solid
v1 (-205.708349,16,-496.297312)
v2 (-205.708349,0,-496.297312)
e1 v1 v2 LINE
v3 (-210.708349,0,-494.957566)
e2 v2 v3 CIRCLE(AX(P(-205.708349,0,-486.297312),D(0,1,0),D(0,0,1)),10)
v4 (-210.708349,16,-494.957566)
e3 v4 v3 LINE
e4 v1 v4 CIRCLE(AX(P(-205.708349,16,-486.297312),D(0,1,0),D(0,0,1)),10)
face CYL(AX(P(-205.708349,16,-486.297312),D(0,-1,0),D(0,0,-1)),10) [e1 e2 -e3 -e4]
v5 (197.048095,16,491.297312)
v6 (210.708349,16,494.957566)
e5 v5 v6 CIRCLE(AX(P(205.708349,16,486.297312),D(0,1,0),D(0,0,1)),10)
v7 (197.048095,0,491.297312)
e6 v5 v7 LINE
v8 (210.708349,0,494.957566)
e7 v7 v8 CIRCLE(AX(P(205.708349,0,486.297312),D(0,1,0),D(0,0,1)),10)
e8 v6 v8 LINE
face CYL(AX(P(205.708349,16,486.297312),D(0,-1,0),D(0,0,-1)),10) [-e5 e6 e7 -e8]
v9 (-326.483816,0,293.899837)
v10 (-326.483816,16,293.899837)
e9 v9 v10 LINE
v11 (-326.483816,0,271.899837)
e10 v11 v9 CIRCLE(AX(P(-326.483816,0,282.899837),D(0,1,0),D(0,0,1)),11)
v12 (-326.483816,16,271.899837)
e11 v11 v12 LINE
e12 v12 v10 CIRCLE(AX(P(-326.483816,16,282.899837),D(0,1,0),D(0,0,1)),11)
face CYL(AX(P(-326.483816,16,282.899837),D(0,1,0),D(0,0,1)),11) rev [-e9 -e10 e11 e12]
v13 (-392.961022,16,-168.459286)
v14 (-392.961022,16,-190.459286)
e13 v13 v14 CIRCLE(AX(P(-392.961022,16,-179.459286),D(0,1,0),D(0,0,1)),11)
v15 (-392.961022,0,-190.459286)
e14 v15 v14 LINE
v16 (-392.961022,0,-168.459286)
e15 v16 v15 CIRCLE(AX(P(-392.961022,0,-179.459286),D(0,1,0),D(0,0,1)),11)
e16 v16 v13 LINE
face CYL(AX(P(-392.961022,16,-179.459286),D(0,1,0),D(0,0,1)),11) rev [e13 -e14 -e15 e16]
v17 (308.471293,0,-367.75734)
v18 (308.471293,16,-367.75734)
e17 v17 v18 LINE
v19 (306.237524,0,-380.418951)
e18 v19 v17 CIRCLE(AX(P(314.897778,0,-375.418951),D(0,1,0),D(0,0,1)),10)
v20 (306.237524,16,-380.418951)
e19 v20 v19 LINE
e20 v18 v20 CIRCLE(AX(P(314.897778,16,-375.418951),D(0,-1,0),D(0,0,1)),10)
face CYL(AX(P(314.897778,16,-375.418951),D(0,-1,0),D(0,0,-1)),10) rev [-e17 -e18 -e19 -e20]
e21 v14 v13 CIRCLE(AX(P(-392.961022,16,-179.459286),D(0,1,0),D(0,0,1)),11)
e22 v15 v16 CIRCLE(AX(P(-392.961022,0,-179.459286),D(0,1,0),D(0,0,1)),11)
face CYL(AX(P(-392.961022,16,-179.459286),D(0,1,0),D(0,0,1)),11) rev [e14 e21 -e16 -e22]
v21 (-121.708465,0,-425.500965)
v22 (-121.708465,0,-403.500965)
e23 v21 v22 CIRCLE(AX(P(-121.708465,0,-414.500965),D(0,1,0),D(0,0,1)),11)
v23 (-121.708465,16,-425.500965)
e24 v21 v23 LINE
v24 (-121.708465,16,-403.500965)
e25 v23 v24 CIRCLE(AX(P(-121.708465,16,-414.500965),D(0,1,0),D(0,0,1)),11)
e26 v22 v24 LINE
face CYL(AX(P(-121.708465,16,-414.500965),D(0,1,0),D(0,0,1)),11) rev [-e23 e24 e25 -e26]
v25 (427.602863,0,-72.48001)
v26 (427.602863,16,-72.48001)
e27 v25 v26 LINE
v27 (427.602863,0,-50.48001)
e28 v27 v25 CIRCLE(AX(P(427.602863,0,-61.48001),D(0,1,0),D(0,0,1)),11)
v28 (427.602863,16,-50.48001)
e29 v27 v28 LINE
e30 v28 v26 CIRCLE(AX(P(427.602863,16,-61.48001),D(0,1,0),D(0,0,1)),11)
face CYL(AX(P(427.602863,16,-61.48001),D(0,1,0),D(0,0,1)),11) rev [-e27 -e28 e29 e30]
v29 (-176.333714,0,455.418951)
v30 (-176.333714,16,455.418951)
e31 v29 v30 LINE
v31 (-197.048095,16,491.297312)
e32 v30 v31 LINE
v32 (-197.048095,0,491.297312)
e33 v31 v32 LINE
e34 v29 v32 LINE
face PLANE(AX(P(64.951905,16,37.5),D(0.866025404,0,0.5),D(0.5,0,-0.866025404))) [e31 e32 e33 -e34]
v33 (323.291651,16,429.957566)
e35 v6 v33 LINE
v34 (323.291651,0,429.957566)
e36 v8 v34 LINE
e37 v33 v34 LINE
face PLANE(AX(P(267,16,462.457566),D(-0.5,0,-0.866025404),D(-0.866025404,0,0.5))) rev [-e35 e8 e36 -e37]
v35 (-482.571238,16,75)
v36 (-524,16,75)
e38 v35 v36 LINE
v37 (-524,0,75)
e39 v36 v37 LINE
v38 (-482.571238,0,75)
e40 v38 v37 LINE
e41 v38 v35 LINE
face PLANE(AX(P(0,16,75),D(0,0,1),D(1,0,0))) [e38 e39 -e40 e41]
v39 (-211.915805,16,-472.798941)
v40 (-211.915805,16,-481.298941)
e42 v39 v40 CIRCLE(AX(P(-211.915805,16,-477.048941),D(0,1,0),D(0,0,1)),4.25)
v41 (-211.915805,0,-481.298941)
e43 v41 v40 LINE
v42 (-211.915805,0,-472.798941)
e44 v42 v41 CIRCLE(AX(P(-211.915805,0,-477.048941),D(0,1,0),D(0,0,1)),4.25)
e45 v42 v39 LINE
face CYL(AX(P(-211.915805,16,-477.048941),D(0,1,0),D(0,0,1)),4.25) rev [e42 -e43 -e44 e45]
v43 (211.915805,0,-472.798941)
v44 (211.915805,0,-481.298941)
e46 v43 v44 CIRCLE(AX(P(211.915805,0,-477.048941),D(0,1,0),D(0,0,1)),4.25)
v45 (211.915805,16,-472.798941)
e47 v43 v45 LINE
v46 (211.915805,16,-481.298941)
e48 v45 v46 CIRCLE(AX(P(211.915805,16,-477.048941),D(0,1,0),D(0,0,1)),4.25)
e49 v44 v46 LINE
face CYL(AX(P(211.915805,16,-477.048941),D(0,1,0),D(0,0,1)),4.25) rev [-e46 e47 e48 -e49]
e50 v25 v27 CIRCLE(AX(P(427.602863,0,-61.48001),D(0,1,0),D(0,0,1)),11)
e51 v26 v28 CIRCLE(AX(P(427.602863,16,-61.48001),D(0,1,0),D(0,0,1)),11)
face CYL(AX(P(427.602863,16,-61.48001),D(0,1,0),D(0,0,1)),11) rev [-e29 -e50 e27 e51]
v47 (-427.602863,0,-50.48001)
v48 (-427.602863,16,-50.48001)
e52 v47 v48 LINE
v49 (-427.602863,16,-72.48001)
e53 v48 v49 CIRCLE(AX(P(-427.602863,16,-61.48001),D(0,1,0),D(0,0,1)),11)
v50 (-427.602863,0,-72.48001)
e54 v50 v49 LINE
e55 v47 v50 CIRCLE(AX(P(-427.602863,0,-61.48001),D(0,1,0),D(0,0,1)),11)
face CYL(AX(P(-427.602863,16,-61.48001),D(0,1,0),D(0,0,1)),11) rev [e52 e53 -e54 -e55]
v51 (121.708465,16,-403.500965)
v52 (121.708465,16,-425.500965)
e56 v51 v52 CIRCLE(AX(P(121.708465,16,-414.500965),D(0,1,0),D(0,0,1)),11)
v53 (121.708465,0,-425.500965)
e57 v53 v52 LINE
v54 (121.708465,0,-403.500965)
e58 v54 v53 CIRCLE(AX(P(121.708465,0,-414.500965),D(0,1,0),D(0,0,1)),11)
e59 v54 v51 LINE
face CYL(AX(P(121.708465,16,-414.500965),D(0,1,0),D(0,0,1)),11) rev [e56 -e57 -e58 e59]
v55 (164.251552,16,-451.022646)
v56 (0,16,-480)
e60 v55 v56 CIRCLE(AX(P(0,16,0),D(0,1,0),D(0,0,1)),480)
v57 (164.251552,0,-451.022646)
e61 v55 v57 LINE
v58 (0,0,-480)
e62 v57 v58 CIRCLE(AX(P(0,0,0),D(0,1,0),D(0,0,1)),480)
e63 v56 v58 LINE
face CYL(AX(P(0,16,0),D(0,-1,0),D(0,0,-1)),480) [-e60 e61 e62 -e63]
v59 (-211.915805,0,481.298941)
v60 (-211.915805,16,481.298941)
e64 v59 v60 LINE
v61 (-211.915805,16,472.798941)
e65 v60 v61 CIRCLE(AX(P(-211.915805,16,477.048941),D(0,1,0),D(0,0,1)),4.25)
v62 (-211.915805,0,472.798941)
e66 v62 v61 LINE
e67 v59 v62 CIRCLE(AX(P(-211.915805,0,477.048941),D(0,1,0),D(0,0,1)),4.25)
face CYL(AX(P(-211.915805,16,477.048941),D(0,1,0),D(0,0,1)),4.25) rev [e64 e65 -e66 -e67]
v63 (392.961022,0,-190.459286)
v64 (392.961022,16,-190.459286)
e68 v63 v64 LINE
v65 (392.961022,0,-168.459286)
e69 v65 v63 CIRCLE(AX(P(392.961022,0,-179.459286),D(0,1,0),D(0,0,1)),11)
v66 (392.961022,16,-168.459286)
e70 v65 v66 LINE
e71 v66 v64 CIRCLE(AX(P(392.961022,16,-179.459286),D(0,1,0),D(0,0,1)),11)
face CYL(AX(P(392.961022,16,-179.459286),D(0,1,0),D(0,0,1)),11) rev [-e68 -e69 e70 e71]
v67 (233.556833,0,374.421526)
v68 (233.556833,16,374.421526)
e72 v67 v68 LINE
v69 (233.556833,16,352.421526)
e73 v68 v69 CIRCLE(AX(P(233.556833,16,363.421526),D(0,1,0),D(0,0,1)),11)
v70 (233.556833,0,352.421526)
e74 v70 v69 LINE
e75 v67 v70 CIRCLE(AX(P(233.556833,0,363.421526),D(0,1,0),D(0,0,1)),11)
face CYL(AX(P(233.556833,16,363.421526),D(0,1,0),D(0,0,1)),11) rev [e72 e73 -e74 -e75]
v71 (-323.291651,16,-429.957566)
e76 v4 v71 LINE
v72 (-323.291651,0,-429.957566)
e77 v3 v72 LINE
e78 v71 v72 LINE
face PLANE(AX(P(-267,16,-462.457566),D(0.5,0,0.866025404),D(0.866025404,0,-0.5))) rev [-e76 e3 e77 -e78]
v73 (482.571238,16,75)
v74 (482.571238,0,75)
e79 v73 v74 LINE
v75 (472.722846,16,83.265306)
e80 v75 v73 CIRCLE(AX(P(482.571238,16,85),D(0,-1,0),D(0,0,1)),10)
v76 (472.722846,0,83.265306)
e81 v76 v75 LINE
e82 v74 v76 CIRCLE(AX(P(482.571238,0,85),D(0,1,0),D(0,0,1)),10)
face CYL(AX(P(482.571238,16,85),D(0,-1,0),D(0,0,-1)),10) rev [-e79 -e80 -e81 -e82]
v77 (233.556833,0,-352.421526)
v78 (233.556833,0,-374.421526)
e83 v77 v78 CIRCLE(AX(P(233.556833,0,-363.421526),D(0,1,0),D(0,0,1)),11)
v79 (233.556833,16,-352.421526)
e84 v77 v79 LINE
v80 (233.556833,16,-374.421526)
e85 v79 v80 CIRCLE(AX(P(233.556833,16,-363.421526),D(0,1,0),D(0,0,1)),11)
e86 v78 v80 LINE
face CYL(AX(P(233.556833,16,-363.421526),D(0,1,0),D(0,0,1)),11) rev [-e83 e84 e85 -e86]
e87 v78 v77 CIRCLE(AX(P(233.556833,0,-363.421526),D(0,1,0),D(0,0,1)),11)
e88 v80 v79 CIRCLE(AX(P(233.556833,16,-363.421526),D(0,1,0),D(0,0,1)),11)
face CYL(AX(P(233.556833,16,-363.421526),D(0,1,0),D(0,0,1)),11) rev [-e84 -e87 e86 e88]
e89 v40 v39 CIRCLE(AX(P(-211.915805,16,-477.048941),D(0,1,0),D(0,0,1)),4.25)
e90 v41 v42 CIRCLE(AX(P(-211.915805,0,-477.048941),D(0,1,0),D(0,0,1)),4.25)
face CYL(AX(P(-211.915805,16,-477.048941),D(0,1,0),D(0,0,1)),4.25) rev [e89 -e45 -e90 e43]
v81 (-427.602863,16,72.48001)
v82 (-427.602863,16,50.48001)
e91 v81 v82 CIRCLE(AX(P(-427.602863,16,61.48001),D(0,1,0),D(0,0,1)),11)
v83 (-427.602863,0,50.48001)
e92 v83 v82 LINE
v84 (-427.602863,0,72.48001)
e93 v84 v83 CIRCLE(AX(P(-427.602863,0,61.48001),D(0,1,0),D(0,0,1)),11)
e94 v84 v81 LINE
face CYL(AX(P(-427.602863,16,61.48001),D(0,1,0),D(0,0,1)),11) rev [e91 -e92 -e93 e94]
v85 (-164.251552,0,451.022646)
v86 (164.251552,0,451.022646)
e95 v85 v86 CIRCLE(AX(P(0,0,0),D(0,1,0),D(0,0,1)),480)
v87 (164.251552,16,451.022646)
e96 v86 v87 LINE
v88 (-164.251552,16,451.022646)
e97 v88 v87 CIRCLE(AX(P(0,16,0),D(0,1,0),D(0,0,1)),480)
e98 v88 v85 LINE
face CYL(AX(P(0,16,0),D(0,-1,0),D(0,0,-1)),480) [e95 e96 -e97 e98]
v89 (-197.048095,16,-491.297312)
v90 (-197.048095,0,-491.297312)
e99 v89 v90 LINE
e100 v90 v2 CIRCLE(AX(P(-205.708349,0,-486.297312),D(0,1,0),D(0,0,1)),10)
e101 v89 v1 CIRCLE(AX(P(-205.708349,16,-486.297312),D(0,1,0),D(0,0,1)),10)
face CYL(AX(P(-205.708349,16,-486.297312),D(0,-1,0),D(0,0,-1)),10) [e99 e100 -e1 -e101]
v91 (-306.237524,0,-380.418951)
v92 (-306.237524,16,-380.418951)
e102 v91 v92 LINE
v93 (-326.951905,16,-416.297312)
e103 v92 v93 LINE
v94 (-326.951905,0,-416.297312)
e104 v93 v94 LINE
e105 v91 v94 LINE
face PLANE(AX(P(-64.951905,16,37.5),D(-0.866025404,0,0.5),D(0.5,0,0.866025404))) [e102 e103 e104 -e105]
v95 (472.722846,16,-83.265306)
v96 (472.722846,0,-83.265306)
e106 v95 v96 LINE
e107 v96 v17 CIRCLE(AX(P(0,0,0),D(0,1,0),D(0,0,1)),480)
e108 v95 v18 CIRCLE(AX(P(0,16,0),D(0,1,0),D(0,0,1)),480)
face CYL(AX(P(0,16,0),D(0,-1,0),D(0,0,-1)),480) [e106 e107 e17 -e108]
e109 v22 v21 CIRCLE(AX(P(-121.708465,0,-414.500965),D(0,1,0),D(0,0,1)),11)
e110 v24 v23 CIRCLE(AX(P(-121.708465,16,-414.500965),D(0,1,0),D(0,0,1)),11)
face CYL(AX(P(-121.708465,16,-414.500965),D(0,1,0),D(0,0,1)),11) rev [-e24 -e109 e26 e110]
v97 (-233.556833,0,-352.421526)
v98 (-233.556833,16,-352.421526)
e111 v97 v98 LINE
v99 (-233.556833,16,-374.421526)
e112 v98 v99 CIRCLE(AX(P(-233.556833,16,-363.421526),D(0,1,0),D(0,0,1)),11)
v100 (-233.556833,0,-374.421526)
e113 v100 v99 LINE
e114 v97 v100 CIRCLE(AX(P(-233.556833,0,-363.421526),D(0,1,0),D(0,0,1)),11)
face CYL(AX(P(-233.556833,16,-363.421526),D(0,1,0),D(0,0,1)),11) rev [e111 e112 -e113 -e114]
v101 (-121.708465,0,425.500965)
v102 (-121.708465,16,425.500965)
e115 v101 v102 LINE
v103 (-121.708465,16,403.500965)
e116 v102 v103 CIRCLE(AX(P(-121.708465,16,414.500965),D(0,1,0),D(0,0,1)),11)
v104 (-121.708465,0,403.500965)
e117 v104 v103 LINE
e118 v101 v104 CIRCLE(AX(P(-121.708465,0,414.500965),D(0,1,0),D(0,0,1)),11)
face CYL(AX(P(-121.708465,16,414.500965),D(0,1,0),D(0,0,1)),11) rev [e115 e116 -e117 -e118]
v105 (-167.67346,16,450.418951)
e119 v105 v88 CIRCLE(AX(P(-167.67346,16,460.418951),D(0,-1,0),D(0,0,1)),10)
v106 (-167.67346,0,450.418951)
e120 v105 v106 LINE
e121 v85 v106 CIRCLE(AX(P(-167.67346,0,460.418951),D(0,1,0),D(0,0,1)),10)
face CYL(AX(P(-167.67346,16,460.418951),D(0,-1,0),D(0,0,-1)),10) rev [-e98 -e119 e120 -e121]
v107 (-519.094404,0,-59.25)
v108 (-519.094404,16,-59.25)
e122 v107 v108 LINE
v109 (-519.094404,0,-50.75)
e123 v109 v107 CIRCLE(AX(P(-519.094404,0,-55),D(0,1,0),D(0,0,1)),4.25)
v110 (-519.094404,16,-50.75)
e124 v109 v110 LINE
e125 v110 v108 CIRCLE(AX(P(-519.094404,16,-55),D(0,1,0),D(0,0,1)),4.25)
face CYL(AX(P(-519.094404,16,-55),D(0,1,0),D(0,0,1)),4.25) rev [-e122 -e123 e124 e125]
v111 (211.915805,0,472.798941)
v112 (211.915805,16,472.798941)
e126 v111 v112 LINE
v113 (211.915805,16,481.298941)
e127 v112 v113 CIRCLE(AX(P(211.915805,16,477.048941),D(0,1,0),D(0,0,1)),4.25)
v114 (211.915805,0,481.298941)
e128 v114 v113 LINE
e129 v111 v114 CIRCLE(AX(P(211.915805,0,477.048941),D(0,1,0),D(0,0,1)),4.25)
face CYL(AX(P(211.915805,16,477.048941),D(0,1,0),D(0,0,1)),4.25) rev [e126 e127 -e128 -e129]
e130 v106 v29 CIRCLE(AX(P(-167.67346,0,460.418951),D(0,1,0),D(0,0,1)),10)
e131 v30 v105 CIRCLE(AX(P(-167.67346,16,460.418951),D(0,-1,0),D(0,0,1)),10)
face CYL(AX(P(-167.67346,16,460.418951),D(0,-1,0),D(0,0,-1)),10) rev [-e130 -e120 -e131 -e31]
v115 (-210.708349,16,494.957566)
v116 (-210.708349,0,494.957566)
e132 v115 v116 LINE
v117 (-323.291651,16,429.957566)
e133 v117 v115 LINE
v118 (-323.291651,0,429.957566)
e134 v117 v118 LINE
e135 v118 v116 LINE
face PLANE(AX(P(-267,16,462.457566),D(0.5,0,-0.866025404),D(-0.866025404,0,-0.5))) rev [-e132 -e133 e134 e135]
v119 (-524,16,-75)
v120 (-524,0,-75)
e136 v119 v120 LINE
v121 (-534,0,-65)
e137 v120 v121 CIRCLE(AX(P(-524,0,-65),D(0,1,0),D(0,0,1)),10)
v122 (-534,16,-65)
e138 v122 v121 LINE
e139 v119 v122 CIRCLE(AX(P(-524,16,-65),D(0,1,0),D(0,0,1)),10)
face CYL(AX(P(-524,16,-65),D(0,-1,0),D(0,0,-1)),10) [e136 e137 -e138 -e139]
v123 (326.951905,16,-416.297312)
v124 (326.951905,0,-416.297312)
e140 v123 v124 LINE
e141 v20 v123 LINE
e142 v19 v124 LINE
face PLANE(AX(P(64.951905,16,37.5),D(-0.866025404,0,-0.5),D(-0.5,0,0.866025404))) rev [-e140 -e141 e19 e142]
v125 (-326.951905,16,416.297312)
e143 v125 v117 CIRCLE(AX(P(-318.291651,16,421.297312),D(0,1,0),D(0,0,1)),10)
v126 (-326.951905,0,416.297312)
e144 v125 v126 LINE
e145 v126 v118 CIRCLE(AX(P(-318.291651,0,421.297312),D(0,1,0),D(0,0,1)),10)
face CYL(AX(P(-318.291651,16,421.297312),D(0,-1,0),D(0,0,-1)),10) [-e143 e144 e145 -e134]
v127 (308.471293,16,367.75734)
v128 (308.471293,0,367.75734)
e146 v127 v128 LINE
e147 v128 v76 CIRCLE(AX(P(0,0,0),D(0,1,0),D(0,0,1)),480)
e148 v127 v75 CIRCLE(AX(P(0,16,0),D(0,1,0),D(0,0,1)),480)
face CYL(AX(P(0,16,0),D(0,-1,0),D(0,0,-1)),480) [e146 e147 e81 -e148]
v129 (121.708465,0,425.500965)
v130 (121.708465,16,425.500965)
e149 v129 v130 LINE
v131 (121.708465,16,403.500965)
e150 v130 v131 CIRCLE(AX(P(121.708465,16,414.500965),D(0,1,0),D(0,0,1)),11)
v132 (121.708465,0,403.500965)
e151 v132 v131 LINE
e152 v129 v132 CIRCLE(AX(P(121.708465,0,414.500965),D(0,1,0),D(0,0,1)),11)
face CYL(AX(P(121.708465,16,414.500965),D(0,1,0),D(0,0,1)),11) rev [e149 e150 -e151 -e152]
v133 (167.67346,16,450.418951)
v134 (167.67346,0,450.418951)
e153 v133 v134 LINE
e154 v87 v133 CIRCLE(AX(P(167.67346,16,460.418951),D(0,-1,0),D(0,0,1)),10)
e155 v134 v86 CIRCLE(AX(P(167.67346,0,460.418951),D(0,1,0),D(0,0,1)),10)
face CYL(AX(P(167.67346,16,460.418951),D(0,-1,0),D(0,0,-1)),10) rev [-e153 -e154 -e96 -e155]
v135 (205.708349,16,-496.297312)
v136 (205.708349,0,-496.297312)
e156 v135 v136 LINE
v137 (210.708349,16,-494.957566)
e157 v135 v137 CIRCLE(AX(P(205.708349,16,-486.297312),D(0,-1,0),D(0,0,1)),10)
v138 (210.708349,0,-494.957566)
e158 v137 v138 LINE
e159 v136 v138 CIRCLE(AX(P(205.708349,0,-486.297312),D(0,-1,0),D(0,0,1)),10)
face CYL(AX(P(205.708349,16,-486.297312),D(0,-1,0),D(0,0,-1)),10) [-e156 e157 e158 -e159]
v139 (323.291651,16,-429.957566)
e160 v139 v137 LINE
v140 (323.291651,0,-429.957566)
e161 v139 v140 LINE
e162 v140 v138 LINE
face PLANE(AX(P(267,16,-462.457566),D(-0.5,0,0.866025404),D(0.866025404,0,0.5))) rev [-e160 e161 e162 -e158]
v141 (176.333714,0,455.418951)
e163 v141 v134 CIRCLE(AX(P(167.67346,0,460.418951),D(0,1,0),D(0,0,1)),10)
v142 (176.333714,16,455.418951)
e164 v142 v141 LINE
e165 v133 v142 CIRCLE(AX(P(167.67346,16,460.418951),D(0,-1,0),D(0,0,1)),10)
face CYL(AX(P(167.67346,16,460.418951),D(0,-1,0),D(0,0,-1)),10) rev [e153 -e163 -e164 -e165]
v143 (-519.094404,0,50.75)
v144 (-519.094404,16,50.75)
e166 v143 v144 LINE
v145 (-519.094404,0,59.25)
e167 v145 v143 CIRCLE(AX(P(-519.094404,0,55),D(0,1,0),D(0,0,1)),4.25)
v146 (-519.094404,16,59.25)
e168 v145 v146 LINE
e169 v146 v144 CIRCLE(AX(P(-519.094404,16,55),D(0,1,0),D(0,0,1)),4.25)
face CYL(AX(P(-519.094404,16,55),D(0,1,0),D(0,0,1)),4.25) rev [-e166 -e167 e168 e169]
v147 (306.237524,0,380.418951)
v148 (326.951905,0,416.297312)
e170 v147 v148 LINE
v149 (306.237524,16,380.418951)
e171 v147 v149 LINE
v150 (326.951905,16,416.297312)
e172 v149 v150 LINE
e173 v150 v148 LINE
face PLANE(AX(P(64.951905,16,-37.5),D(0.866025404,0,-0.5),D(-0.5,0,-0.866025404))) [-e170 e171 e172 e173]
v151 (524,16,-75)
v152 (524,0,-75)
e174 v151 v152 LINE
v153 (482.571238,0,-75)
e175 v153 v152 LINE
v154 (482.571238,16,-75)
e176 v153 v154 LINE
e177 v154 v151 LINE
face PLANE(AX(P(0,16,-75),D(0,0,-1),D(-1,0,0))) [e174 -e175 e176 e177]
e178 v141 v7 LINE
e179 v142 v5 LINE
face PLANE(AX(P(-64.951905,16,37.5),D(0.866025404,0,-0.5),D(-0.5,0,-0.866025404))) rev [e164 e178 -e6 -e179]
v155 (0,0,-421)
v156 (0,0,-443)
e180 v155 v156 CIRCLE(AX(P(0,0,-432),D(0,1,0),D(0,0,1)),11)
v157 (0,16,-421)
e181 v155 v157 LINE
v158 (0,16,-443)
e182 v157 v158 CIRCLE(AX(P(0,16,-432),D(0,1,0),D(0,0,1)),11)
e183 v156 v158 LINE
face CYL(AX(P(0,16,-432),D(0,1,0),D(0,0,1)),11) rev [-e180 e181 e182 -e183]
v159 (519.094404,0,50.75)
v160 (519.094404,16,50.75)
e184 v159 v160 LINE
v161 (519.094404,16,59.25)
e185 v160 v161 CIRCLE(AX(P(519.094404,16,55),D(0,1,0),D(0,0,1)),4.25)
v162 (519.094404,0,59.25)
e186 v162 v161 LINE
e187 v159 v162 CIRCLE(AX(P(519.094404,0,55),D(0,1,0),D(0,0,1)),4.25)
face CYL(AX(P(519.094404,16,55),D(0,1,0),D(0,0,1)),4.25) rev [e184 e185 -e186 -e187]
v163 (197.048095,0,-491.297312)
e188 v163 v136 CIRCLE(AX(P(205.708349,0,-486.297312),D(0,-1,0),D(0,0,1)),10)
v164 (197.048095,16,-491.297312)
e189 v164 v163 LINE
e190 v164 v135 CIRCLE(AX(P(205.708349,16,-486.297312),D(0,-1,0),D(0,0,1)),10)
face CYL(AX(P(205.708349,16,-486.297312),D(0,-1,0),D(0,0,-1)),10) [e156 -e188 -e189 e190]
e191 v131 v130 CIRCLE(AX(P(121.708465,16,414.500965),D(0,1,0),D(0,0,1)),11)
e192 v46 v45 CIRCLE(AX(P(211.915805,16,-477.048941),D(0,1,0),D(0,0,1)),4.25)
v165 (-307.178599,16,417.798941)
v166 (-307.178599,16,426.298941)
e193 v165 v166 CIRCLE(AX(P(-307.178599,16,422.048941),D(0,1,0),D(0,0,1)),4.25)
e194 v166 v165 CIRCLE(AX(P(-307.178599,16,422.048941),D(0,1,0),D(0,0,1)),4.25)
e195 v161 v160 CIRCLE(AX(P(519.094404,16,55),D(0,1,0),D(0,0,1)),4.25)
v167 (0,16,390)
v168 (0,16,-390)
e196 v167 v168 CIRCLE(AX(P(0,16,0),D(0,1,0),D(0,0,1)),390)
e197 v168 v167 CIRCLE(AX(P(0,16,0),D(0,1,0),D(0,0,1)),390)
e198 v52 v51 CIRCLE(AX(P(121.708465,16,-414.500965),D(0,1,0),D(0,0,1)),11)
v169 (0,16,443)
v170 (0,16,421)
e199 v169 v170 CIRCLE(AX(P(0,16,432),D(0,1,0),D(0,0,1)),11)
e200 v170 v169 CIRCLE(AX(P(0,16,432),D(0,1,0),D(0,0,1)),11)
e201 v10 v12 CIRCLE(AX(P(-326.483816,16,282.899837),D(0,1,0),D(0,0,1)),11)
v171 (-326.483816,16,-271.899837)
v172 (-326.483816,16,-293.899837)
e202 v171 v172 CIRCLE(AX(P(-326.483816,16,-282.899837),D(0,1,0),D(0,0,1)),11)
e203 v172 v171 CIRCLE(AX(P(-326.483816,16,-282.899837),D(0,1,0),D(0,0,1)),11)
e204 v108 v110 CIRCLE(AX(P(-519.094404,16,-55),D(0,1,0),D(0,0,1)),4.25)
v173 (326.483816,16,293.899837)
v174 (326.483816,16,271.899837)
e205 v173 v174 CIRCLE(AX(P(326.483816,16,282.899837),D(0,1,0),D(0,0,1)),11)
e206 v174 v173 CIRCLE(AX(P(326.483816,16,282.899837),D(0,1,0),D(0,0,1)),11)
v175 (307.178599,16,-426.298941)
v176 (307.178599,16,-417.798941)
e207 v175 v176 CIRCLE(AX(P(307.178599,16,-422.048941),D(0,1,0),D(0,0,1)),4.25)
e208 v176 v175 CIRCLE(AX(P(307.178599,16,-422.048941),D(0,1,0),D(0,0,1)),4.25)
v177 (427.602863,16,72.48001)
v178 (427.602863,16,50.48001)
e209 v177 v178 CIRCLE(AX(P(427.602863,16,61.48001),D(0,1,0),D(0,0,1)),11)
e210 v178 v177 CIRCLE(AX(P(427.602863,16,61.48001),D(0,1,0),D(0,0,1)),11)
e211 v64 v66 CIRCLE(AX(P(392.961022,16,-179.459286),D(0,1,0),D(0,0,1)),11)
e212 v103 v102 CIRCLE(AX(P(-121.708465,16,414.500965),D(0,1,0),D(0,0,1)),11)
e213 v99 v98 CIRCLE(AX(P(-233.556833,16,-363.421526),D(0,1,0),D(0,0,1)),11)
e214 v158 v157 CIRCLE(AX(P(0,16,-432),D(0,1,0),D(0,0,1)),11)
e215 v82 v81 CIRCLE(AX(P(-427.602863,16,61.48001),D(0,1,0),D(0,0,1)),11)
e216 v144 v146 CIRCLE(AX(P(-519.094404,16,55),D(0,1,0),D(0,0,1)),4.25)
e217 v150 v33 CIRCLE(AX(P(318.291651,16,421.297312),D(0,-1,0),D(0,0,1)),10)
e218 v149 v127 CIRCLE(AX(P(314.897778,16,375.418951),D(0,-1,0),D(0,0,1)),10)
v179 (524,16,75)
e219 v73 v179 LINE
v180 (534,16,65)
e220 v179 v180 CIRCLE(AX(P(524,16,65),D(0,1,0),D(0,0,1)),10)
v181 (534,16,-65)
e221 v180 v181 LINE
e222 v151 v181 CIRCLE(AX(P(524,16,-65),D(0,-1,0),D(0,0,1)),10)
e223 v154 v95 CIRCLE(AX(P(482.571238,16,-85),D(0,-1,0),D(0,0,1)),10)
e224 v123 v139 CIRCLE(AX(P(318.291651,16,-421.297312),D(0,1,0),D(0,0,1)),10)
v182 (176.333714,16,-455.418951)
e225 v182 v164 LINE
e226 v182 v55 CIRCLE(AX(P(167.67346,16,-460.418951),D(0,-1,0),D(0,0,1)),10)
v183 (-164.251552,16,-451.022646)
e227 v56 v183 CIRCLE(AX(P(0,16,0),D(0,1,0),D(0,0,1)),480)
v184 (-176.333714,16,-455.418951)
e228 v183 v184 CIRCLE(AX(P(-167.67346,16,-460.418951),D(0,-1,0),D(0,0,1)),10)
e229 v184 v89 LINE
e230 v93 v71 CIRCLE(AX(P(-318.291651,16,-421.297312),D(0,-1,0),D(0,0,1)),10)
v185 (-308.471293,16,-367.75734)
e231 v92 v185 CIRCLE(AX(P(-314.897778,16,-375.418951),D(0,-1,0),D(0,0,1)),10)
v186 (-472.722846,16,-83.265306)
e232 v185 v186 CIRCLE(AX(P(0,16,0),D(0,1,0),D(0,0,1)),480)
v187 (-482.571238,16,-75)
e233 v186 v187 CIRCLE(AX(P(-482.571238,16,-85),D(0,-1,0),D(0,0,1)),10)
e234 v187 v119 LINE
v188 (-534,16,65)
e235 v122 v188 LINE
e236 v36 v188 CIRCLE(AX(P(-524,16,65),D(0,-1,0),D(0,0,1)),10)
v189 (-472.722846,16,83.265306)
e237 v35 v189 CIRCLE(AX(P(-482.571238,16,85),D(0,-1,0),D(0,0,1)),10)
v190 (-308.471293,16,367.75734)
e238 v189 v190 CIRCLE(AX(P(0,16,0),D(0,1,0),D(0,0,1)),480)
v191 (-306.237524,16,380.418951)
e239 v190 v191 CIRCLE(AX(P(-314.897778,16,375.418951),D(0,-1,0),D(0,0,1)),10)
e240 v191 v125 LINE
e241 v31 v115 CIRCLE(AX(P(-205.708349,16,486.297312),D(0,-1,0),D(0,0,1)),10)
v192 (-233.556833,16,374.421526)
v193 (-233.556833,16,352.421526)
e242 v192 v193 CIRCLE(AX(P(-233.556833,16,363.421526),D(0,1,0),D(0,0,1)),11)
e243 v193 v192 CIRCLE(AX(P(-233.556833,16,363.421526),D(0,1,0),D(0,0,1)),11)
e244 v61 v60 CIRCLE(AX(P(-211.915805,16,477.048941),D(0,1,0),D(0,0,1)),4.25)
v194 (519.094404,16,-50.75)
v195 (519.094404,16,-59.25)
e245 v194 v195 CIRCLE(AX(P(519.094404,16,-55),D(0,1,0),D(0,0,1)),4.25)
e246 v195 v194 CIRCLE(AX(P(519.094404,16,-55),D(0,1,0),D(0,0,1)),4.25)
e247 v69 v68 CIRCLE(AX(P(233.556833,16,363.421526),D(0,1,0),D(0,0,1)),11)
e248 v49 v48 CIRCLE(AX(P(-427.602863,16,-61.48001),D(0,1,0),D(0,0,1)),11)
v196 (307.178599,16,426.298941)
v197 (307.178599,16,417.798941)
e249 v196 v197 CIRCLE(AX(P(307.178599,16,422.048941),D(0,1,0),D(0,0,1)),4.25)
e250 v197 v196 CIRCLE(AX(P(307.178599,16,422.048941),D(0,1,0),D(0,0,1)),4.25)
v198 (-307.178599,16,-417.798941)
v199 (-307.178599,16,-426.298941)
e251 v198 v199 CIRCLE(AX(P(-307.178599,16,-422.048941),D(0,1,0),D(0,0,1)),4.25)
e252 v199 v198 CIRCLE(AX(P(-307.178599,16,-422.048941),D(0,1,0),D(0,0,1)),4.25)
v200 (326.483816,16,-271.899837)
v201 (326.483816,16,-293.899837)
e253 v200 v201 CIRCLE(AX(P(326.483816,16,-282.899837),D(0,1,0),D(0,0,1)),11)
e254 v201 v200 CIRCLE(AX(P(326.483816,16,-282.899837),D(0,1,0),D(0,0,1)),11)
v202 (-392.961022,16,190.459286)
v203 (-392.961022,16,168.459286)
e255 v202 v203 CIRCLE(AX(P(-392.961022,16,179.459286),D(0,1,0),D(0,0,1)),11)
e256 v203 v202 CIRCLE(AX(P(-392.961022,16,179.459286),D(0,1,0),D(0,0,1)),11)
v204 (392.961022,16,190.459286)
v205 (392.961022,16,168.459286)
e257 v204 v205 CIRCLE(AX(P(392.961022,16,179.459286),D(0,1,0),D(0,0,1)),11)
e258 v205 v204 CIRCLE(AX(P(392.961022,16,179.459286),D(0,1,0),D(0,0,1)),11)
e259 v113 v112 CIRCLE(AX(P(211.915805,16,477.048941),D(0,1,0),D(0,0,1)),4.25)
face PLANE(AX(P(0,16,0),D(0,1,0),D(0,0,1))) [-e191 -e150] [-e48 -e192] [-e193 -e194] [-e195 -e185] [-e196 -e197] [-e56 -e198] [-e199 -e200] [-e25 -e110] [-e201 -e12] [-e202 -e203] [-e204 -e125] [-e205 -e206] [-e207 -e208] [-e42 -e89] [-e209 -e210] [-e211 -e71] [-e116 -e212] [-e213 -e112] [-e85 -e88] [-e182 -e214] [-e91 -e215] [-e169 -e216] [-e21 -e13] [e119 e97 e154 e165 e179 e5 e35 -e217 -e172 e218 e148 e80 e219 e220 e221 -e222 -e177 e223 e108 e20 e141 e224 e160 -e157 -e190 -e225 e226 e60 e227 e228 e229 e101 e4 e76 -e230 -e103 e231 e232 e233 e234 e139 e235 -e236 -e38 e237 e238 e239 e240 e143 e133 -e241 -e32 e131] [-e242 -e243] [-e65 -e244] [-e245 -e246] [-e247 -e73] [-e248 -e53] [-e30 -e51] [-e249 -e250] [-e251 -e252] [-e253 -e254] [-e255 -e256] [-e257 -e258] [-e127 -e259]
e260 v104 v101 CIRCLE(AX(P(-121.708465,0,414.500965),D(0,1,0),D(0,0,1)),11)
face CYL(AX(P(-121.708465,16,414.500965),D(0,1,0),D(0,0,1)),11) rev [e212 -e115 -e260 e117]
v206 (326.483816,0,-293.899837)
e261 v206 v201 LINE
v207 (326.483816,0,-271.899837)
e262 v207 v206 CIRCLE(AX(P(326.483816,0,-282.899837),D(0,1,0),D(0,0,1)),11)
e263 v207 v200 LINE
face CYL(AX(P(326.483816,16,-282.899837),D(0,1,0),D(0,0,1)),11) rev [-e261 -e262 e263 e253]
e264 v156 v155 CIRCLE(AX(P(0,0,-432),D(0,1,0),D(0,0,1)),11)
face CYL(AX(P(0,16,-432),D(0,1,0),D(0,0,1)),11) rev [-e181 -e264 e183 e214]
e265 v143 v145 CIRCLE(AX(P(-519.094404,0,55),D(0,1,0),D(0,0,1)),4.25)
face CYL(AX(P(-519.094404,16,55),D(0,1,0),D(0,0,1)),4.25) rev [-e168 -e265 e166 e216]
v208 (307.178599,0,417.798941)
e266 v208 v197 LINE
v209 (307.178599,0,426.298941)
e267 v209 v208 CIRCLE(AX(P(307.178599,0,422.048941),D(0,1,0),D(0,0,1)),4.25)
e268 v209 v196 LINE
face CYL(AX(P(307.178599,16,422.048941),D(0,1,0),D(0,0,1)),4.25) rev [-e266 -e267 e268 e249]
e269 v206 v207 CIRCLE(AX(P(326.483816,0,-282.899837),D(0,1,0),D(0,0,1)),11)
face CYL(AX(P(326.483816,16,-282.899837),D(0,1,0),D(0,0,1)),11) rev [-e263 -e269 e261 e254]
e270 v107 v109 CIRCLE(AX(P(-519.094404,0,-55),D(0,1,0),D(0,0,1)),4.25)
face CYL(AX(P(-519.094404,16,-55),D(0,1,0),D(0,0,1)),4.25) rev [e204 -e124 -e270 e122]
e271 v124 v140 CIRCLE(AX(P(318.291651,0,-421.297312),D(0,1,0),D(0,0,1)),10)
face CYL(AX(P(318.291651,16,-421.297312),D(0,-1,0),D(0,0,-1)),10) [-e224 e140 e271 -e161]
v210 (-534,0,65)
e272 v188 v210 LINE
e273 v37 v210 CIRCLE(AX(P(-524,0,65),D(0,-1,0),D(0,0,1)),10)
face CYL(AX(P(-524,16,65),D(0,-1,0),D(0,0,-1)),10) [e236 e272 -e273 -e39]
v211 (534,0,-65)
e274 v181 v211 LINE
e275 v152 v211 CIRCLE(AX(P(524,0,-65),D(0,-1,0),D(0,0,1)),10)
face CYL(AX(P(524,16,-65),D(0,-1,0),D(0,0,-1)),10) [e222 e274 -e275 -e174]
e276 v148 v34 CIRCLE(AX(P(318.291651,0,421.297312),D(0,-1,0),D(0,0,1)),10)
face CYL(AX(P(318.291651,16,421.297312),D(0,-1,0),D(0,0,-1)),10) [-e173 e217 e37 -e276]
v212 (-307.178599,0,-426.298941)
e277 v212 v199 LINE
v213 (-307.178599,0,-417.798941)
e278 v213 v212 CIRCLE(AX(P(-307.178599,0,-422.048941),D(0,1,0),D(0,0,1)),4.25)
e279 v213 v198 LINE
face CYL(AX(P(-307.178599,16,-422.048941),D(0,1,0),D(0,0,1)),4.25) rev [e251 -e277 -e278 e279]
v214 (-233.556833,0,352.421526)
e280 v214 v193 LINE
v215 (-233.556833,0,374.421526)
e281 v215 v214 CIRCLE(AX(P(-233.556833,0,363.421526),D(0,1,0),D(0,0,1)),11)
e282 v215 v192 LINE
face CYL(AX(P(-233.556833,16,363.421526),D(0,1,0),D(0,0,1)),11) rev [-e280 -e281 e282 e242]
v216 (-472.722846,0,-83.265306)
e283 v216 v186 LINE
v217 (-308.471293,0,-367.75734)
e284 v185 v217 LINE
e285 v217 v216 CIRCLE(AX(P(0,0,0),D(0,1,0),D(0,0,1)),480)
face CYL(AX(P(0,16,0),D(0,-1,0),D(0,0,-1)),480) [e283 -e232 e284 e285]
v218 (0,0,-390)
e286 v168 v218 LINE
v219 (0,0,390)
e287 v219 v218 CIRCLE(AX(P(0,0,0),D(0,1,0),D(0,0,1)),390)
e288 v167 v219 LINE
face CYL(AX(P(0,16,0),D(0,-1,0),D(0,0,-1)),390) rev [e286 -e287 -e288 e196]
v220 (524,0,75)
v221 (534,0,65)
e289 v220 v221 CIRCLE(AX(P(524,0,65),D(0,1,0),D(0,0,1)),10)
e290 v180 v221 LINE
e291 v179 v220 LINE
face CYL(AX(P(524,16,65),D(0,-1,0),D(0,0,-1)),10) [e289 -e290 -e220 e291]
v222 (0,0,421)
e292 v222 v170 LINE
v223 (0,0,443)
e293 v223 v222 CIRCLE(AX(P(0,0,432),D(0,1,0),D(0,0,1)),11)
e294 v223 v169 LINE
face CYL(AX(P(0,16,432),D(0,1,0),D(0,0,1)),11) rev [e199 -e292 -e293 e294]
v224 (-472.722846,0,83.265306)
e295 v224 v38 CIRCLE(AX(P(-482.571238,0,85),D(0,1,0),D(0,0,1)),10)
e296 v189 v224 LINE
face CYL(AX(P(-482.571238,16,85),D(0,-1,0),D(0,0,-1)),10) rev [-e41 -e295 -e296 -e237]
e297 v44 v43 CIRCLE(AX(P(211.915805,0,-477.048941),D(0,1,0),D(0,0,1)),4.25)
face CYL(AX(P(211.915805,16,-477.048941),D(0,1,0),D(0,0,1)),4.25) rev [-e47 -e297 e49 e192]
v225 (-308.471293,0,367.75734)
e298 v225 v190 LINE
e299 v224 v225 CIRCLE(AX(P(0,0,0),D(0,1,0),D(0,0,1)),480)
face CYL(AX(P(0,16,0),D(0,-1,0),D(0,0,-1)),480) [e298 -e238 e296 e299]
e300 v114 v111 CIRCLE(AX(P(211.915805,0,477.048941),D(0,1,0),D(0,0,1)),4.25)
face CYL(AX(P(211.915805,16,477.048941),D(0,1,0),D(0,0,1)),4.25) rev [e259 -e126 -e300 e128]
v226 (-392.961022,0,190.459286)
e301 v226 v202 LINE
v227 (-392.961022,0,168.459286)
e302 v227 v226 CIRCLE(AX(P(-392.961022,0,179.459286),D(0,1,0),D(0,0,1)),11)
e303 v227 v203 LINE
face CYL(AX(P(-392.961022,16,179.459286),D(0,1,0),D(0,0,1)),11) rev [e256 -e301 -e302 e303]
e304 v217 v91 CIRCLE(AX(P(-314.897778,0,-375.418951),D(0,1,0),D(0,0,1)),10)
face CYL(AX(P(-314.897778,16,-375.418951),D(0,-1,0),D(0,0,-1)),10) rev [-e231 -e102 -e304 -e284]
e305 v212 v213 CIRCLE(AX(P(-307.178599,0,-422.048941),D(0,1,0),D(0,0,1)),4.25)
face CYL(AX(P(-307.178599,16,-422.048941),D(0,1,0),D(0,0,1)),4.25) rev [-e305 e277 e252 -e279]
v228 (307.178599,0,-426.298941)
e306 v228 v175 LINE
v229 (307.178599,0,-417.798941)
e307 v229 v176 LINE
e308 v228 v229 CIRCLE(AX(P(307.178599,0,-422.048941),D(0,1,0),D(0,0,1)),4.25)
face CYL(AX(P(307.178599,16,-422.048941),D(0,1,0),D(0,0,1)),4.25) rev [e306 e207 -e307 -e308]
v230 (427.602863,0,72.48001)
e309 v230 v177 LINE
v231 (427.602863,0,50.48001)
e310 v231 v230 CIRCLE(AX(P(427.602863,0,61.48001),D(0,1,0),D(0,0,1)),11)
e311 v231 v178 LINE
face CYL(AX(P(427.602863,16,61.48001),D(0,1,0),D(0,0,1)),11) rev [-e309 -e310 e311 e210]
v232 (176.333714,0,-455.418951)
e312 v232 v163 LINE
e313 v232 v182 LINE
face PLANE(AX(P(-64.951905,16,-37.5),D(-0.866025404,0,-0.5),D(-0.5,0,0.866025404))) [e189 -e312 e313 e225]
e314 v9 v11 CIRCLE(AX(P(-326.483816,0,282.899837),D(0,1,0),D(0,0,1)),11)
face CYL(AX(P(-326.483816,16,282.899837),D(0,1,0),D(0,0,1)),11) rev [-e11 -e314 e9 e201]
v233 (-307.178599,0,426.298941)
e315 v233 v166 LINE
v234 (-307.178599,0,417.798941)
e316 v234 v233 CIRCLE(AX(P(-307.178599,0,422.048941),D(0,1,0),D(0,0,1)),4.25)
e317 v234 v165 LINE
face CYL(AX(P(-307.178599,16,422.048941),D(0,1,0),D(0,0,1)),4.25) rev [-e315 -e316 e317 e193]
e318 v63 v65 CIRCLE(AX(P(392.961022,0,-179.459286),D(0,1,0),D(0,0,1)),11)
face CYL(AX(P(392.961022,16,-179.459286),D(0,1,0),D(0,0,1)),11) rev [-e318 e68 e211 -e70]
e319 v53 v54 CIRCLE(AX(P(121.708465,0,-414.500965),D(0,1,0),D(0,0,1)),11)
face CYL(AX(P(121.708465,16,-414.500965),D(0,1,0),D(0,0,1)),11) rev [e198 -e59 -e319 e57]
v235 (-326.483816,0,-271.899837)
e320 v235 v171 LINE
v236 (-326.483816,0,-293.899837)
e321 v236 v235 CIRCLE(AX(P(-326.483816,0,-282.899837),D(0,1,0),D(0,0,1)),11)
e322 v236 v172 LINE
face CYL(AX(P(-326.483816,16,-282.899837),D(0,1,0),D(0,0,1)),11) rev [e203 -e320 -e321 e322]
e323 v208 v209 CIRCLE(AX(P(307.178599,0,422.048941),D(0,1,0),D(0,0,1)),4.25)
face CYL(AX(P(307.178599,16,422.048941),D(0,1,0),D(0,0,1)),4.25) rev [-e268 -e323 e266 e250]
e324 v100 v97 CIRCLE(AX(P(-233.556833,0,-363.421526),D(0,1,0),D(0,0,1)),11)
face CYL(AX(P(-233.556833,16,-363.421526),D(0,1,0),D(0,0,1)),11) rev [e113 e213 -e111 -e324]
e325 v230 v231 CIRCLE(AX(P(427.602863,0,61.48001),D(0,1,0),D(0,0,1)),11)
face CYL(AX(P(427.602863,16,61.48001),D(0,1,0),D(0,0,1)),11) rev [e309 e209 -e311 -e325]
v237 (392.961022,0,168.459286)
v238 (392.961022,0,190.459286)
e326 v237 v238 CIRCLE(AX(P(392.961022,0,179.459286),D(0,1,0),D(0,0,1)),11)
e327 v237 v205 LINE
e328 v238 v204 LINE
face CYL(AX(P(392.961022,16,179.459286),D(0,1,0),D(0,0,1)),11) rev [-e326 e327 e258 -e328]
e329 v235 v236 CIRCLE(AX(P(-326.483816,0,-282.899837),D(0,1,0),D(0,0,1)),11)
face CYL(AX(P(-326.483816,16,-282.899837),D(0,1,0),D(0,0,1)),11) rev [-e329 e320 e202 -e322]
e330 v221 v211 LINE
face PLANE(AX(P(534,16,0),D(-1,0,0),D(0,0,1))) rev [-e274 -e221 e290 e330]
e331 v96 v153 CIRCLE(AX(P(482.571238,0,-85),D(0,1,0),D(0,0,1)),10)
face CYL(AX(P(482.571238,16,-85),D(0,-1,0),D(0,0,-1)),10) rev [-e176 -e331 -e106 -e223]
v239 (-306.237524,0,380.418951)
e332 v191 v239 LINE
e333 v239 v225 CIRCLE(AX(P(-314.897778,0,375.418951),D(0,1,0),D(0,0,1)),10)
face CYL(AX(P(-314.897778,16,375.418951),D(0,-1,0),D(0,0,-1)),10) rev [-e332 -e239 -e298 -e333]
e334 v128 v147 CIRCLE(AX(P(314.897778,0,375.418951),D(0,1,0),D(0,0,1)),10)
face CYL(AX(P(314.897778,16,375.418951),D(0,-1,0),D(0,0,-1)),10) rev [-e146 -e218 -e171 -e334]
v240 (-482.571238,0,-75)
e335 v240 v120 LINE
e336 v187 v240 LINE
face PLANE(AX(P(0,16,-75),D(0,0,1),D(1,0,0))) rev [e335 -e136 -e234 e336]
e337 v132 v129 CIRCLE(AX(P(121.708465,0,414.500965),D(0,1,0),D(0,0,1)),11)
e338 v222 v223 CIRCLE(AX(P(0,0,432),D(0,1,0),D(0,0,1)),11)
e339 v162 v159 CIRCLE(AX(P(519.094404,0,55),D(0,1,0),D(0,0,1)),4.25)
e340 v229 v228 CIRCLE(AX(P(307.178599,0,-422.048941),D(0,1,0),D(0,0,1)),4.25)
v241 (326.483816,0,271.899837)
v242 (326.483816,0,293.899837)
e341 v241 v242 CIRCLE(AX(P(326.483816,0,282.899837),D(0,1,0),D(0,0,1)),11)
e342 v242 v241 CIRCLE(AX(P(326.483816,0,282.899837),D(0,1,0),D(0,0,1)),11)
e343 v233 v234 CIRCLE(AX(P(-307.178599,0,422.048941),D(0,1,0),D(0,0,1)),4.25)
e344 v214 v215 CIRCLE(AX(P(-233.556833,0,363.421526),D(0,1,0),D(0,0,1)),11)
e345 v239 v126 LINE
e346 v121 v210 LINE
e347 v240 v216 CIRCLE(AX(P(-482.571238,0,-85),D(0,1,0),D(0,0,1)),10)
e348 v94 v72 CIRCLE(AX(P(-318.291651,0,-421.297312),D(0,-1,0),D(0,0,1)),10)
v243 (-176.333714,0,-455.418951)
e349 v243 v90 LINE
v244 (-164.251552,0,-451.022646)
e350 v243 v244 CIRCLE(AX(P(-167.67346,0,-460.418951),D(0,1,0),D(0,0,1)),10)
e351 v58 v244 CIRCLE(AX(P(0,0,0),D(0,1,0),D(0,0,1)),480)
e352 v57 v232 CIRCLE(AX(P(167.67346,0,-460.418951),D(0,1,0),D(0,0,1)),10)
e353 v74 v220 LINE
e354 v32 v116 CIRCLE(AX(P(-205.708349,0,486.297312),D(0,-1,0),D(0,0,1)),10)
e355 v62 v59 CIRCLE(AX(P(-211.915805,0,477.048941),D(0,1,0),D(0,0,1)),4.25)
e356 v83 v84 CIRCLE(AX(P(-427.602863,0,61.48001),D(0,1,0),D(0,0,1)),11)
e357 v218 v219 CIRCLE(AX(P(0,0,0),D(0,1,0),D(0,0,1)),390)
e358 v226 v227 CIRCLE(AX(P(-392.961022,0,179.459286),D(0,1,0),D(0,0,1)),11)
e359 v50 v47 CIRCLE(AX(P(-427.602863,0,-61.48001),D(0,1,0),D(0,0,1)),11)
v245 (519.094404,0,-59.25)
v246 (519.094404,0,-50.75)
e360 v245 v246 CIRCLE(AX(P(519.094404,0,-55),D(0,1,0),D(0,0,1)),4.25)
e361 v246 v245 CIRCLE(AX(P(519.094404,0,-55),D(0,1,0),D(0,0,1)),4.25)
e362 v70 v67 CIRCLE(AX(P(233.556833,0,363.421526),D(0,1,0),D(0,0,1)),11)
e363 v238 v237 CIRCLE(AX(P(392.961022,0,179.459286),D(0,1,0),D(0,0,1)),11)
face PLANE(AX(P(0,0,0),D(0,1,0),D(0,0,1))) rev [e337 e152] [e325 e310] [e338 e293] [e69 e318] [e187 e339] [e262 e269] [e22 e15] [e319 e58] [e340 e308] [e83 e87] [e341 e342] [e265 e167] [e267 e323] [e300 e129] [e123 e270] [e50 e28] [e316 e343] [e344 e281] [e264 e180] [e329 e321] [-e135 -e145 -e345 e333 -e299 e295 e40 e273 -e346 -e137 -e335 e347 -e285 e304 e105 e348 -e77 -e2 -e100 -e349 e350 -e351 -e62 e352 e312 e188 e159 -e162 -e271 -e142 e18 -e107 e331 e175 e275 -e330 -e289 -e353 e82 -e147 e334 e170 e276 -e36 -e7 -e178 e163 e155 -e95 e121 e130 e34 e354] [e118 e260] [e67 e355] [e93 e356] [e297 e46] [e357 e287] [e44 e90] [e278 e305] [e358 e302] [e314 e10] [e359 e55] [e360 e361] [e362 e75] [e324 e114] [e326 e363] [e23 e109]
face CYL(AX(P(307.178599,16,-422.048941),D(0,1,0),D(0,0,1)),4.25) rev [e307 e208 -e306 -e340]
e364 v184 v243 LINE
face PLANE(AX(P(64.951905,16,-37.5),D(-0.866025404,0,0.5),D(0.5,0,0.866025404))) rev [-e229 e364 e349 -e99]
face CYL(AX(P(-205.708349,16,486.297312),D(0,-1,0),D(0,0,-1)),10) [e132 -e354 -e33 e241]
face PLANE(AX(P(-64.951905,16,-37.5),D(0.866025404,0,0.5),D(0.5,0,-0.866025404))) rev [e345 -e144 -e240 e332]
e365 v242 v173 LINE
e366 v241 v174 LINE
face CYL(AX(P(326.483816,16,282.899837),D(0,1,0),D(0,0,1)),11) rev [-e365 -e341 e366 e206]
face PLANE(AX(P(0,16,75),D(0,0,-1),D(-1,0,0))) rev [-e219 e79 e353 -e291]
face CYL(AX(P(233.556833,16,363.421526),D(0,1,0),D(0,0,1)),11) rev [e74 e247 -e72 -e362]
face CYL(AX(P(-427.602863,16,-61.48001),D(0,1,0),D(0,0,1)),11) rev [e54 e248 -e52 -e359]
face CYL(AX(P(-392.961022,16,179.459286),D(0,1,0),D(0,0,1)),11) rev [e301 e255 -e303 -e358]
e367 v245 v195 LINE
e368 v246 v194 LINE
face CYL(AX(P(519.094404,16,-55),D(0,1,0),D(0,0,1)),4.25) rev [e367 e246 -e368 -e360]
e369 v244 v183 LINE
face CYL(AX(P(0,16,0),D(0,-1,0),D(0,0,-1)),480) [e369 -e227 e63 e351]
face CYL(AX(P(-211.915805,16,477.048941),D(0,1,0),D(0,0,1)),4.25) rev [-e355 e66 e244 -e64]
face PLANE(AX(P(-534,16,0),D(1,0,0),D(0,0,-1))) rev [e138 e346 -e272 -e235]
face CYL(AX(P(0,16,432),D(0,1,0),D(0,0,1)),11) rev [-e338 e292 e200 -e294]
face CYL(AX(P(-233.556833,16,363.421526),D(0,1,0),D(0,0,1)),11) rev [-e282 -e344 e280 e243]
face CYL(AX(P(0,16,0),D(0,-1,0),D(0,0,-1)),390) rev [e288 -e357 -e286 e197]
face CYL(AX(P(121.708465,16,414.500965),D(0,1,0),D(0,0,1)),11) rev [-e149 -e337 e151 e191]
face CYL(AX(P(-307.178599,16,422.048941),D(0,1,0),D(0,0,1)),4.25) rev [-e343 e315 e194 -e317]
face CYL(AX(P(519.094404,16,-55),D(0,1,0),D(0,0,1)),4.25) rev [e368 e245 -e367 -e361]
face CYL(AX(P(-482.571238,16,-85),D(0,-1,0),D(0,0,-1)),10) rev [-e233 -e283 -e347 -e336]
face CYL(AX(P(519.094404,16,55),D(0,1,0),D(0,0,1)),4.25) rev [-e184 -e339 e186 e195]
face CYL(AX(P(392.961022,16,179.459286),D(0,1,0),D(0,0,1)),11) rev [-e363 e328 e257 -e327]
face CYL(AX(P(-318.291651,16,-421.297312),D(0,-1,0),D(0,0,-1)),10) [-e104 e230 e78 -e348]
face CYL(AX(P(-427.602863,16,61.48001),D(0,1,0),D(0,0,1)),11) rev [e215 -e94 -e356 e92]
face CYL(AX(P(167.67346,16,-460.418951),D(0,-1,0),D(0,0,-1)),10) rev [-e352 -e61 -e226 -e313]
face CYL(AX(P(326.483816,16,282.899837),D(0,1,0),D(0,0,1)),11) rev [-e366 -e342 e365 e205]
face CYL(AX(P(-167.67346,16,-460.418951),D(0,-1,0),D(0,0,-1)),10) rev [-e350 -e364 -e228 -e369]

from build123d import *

# Parameters (mm, degrees)
SKETCH2_R                  = 480
SKETCH2_R_2                = 390
BOSS_EXTRUDE1_DEPTH        = 16
FILLET1_R                  = 10
F_22_0_22_DIAMETER_HOLE1_D = 22
M10_TAPPED_HOLE1_D         = 8.5


with BuildPart() as part:
    # Sketch2 → Boss-Extrude1 (new body)
    # profile 1 of 7: a face of its own
    with BuildSketch(Plane(origin=(0, 0, 0), x_dir=(1, 0, 0), z_dir=(0, 1, 0))):
        Circle(SKETCH2_R)
        with Locations(Location((0, 0, 0), (0, 0, 270))):
            Circle(SKETCH2_R_2, mode=Mode.SUBTRACT)
    # profile 2 of 7: a face of its own
    with BuildSketch(Plane(origin=(0, 0, 0), x_dir=(1, 0, 0), z_dir=(0, 1, 0))):
        with BuildLine():
            Line((-326.951905284, 416.297311583), (-302.004114723, 373.086470795))
            ThreePointArc((-302.004114723, 373.086470795), (-240, 415.692193817), (-172.100304155, 448.086470795))
            Line((-172.100304155, 448.086470795), (-197.048094716, 491.297311583))
            ThreePointArc((-197.048094716, 491.297311583), (-203.120158303, 495.956569846), (-210.708348754, 494.957565621))
            Line((-210.708348754, 494.957565621), (-323.291651246, 429.957565621))
            ThreePointArc((-323.291651246, 429.957565621), (-327.950909509, 423.885502034), (-326.951905284, 416.297311583))
        make_face()
    # profile 3 of 7: a face of its own
    with BuildSketch(Plane(origin=(0, 0, 0), x_dir=(1, 0, 0), z_dir=(0, 1, 0))):
        with BuildLine():
            ThreePointArc((-474.104418878, -75), (-480, 0), (-474.104418878, 75))
            Line((-474.104418878, 75), (-524, 75))
            ThreePointArc((-524, 75), (-531.071067812, 72.071067812), (-534, 65))
            Line((-534, 65), (-534, -65))
            ThreePointArc((-534, -65), (-531.071067812, -72.071067812), (-524, -75))
            Line((-524, -75), (-474.104418878, -75))
        make_face()
    # profile 4 of 7: a face of its own
    with BuildSketch(Plane(origin=(0, 0, 0), x_dir=(1, 0, 0), z_dir=(0, 1, 0))):
        with BuildLine():
            ThreePointArc((-172.100304155, -448.086470795), (-240, -415.692193817), (-302.004114723, -373.086470795))
            Line((-302.004114723, -373.086470795), (-326.951905284, -416.297311583))
            ThreePointArc((-326.951905284, -416.297311583), (-327.950909509, -423.885502034), (-323.291651246, -429.957565621))
            Line((-323.291651246, -429.957565621), (-210.708348754, -494.957565621))
            ThreePointArc((-210.708348754, -494.957565621), (-203.120158303, -495.956569846), (-197.048094716, -491.297311583))
            Line((-197.048094716, -491.297311583), (-172.100304155, -448.086470795))
        make_face()
    # profile 5 of 7: a face of its own
    with BuildSketch(Plane(origin=(0, 0, 0), x_dir=(1, 0, 0), z_dir=(0, 1, 0))):
        with BuildLine():
            ThreePointArc((302.004114723, -373.086470795), (240, -415.692193817), (172.100304155, -448.086470795))
            Line((172.100304155, -448.086470795), (197.048094716, -491.297311583))
            ThreePointArc((197.048094716, -491.297311583), (203.120158303, -495.956569846), (210.708348754, -494.957565621))
            Line((210.708348754, -494.957565621), (323.291651246, -429.957565621))
            ThreePointArc((323.291651246, -429.957565621), (327.950909509, -423.885502034), (326.951905284, -416.297311583))
            Line((326.951905284, -416.297311583), (302.004114723, -373.086470795))
        make_face()
    # profile 6 of 7: a face of its own
    with BuildSketch(Plane(origin=(0, 0, 0), x_dir=(1, 0, 0), z_dir=(0, 1, 0))):
        with BuildLine():
            Line((524, 75), (474.104418878, 75))
            ThreePointArc((474.104418878, 75), (478.523834862, 37.615681161), (480, 0))
            ThreePointArc((480, 0), (478.523834862, -37.615681161), (474.104418878, -75))
            Line((474.104418878, -75), (524, -75))
            ThreePointArc((524, -75), (531.071067812, -72.071067812), (534, -65))
            Line((534, -65), (534, 65))
            ThreePointArc((534, 65), (531.071067812, 72.071067812), (524, 75))
        make_face()
    # profile 7 of 7: a face of its own
    with BuildSketch(Plane(origin=(0, 0, 0), x_dir=(1, 0, 0), z_dir=(0, 1, 0))):
        with BuildLine():
            Line((197.048094716, 491.297311583), (172.100304155, 448.086470795))
            ThreePointArc((172.100304155, 448.086470795), (240, 415.692193817), (302.004114723, 373.086470795))
            Line((302.004114723, 373.086470795), (326.951905284, 416.297311583))
            ThreePointArc((326.951905284, 416.297311583), (327.950909509, 423.885502034), (323.291651246, 429.957565621))
            Line((323.291651246, 429.957565621), (210.708348754, 494.957565621))
            ThreePointArc((210.708348754, 494.957565621), (203.120158303, 495.956569846), (197.048094716, 491.297311583))
        make_face()
    extrude(amount=BOSS_EXTRUDE1_DEPTH)

    # Fillet1
    fillet1_edges = [part.edges().sort_by_distance(p)[0] for p in [
        (-172.100304155, 8, 448.086470795),
        (-302.004114723, 8, 373.086470795),
        (-474.104418878, 8, 75),
        (-474.104418878, 8, -75),
        (-302.004114723, 8, -373.086470795),
        (-172.100304155, 8, -448.086470795),
        (172.100304155, 8, -448.086470795),
        (302.004114723, 8, -373.086470795),
        (474.104418878, 8, -75),
        (474.104418878, 8, 75),
        (302.004114723, 8, 373.086470795),
        (172.100304155, 8, 448.086470795),
    ]]
    fillet(fillet1_edges, radius=FILLET1_R)

    # Ø22.0 (22) Diameter Hole1 (through all)
    with Locations(Plane(origin=(0, 16, 0), x_dir=(1, 0, 0), z_dir=(0, 1, 0))):
        with Locations((0, 432), (121.708464555, 414.500964601), (233.556833141, 363.421526183), (326.483816121, 282.899837064), (392.961021993, 179.459285617), (427.602862893, 61.480010134), (427.602862893, -61.480010134), (392.961021993, -179.459285617), (326.483816121, -282.899837064), (233.556833141, -363.421526183), (121.708464555, -414.500964601), (0, -432), (-121.708464555, -414.500964601), (-233.556833141, -363.421526183), (-326.483816121, -282.899837064), (-392.961021993, -179.459285617), (-427.602862893, -61.480010134), (-427.602862893, 61.480010134), (-392.961021993, 179.459285617), (-326.483816121, 282.899837064), (-233.556833141, 363.421526183), (-121.708464555, 414.500964601)):
            Hole(F_22_0_22_DIAMETER_HOLE1_D / 2)

    # M10 Tapped Hole1 (through all)
    with Locations(Plane(origin=(0, 16, 0), x_dir=(1, 0, 0), z_dir=(0, 1, 0))):
        with Locations((-519.094403746, 55), (-519.094403746, -55), (-211.915804665, 477.048940606), (-307.178599081, 422.048940606), (307.178599081, 422.048940606), (211.915804665, 477.048940606), (519.094403746, -55), (519.094403746, 55), (211.915804665, -477.048940606), (307.178599081, -422.048940606), (-307.178599081, -422.048940606), (-211.915804665, -477.048940606)):
            Hole(M10_TAPPED_HOLE1_D / 2)


solid = part.part
